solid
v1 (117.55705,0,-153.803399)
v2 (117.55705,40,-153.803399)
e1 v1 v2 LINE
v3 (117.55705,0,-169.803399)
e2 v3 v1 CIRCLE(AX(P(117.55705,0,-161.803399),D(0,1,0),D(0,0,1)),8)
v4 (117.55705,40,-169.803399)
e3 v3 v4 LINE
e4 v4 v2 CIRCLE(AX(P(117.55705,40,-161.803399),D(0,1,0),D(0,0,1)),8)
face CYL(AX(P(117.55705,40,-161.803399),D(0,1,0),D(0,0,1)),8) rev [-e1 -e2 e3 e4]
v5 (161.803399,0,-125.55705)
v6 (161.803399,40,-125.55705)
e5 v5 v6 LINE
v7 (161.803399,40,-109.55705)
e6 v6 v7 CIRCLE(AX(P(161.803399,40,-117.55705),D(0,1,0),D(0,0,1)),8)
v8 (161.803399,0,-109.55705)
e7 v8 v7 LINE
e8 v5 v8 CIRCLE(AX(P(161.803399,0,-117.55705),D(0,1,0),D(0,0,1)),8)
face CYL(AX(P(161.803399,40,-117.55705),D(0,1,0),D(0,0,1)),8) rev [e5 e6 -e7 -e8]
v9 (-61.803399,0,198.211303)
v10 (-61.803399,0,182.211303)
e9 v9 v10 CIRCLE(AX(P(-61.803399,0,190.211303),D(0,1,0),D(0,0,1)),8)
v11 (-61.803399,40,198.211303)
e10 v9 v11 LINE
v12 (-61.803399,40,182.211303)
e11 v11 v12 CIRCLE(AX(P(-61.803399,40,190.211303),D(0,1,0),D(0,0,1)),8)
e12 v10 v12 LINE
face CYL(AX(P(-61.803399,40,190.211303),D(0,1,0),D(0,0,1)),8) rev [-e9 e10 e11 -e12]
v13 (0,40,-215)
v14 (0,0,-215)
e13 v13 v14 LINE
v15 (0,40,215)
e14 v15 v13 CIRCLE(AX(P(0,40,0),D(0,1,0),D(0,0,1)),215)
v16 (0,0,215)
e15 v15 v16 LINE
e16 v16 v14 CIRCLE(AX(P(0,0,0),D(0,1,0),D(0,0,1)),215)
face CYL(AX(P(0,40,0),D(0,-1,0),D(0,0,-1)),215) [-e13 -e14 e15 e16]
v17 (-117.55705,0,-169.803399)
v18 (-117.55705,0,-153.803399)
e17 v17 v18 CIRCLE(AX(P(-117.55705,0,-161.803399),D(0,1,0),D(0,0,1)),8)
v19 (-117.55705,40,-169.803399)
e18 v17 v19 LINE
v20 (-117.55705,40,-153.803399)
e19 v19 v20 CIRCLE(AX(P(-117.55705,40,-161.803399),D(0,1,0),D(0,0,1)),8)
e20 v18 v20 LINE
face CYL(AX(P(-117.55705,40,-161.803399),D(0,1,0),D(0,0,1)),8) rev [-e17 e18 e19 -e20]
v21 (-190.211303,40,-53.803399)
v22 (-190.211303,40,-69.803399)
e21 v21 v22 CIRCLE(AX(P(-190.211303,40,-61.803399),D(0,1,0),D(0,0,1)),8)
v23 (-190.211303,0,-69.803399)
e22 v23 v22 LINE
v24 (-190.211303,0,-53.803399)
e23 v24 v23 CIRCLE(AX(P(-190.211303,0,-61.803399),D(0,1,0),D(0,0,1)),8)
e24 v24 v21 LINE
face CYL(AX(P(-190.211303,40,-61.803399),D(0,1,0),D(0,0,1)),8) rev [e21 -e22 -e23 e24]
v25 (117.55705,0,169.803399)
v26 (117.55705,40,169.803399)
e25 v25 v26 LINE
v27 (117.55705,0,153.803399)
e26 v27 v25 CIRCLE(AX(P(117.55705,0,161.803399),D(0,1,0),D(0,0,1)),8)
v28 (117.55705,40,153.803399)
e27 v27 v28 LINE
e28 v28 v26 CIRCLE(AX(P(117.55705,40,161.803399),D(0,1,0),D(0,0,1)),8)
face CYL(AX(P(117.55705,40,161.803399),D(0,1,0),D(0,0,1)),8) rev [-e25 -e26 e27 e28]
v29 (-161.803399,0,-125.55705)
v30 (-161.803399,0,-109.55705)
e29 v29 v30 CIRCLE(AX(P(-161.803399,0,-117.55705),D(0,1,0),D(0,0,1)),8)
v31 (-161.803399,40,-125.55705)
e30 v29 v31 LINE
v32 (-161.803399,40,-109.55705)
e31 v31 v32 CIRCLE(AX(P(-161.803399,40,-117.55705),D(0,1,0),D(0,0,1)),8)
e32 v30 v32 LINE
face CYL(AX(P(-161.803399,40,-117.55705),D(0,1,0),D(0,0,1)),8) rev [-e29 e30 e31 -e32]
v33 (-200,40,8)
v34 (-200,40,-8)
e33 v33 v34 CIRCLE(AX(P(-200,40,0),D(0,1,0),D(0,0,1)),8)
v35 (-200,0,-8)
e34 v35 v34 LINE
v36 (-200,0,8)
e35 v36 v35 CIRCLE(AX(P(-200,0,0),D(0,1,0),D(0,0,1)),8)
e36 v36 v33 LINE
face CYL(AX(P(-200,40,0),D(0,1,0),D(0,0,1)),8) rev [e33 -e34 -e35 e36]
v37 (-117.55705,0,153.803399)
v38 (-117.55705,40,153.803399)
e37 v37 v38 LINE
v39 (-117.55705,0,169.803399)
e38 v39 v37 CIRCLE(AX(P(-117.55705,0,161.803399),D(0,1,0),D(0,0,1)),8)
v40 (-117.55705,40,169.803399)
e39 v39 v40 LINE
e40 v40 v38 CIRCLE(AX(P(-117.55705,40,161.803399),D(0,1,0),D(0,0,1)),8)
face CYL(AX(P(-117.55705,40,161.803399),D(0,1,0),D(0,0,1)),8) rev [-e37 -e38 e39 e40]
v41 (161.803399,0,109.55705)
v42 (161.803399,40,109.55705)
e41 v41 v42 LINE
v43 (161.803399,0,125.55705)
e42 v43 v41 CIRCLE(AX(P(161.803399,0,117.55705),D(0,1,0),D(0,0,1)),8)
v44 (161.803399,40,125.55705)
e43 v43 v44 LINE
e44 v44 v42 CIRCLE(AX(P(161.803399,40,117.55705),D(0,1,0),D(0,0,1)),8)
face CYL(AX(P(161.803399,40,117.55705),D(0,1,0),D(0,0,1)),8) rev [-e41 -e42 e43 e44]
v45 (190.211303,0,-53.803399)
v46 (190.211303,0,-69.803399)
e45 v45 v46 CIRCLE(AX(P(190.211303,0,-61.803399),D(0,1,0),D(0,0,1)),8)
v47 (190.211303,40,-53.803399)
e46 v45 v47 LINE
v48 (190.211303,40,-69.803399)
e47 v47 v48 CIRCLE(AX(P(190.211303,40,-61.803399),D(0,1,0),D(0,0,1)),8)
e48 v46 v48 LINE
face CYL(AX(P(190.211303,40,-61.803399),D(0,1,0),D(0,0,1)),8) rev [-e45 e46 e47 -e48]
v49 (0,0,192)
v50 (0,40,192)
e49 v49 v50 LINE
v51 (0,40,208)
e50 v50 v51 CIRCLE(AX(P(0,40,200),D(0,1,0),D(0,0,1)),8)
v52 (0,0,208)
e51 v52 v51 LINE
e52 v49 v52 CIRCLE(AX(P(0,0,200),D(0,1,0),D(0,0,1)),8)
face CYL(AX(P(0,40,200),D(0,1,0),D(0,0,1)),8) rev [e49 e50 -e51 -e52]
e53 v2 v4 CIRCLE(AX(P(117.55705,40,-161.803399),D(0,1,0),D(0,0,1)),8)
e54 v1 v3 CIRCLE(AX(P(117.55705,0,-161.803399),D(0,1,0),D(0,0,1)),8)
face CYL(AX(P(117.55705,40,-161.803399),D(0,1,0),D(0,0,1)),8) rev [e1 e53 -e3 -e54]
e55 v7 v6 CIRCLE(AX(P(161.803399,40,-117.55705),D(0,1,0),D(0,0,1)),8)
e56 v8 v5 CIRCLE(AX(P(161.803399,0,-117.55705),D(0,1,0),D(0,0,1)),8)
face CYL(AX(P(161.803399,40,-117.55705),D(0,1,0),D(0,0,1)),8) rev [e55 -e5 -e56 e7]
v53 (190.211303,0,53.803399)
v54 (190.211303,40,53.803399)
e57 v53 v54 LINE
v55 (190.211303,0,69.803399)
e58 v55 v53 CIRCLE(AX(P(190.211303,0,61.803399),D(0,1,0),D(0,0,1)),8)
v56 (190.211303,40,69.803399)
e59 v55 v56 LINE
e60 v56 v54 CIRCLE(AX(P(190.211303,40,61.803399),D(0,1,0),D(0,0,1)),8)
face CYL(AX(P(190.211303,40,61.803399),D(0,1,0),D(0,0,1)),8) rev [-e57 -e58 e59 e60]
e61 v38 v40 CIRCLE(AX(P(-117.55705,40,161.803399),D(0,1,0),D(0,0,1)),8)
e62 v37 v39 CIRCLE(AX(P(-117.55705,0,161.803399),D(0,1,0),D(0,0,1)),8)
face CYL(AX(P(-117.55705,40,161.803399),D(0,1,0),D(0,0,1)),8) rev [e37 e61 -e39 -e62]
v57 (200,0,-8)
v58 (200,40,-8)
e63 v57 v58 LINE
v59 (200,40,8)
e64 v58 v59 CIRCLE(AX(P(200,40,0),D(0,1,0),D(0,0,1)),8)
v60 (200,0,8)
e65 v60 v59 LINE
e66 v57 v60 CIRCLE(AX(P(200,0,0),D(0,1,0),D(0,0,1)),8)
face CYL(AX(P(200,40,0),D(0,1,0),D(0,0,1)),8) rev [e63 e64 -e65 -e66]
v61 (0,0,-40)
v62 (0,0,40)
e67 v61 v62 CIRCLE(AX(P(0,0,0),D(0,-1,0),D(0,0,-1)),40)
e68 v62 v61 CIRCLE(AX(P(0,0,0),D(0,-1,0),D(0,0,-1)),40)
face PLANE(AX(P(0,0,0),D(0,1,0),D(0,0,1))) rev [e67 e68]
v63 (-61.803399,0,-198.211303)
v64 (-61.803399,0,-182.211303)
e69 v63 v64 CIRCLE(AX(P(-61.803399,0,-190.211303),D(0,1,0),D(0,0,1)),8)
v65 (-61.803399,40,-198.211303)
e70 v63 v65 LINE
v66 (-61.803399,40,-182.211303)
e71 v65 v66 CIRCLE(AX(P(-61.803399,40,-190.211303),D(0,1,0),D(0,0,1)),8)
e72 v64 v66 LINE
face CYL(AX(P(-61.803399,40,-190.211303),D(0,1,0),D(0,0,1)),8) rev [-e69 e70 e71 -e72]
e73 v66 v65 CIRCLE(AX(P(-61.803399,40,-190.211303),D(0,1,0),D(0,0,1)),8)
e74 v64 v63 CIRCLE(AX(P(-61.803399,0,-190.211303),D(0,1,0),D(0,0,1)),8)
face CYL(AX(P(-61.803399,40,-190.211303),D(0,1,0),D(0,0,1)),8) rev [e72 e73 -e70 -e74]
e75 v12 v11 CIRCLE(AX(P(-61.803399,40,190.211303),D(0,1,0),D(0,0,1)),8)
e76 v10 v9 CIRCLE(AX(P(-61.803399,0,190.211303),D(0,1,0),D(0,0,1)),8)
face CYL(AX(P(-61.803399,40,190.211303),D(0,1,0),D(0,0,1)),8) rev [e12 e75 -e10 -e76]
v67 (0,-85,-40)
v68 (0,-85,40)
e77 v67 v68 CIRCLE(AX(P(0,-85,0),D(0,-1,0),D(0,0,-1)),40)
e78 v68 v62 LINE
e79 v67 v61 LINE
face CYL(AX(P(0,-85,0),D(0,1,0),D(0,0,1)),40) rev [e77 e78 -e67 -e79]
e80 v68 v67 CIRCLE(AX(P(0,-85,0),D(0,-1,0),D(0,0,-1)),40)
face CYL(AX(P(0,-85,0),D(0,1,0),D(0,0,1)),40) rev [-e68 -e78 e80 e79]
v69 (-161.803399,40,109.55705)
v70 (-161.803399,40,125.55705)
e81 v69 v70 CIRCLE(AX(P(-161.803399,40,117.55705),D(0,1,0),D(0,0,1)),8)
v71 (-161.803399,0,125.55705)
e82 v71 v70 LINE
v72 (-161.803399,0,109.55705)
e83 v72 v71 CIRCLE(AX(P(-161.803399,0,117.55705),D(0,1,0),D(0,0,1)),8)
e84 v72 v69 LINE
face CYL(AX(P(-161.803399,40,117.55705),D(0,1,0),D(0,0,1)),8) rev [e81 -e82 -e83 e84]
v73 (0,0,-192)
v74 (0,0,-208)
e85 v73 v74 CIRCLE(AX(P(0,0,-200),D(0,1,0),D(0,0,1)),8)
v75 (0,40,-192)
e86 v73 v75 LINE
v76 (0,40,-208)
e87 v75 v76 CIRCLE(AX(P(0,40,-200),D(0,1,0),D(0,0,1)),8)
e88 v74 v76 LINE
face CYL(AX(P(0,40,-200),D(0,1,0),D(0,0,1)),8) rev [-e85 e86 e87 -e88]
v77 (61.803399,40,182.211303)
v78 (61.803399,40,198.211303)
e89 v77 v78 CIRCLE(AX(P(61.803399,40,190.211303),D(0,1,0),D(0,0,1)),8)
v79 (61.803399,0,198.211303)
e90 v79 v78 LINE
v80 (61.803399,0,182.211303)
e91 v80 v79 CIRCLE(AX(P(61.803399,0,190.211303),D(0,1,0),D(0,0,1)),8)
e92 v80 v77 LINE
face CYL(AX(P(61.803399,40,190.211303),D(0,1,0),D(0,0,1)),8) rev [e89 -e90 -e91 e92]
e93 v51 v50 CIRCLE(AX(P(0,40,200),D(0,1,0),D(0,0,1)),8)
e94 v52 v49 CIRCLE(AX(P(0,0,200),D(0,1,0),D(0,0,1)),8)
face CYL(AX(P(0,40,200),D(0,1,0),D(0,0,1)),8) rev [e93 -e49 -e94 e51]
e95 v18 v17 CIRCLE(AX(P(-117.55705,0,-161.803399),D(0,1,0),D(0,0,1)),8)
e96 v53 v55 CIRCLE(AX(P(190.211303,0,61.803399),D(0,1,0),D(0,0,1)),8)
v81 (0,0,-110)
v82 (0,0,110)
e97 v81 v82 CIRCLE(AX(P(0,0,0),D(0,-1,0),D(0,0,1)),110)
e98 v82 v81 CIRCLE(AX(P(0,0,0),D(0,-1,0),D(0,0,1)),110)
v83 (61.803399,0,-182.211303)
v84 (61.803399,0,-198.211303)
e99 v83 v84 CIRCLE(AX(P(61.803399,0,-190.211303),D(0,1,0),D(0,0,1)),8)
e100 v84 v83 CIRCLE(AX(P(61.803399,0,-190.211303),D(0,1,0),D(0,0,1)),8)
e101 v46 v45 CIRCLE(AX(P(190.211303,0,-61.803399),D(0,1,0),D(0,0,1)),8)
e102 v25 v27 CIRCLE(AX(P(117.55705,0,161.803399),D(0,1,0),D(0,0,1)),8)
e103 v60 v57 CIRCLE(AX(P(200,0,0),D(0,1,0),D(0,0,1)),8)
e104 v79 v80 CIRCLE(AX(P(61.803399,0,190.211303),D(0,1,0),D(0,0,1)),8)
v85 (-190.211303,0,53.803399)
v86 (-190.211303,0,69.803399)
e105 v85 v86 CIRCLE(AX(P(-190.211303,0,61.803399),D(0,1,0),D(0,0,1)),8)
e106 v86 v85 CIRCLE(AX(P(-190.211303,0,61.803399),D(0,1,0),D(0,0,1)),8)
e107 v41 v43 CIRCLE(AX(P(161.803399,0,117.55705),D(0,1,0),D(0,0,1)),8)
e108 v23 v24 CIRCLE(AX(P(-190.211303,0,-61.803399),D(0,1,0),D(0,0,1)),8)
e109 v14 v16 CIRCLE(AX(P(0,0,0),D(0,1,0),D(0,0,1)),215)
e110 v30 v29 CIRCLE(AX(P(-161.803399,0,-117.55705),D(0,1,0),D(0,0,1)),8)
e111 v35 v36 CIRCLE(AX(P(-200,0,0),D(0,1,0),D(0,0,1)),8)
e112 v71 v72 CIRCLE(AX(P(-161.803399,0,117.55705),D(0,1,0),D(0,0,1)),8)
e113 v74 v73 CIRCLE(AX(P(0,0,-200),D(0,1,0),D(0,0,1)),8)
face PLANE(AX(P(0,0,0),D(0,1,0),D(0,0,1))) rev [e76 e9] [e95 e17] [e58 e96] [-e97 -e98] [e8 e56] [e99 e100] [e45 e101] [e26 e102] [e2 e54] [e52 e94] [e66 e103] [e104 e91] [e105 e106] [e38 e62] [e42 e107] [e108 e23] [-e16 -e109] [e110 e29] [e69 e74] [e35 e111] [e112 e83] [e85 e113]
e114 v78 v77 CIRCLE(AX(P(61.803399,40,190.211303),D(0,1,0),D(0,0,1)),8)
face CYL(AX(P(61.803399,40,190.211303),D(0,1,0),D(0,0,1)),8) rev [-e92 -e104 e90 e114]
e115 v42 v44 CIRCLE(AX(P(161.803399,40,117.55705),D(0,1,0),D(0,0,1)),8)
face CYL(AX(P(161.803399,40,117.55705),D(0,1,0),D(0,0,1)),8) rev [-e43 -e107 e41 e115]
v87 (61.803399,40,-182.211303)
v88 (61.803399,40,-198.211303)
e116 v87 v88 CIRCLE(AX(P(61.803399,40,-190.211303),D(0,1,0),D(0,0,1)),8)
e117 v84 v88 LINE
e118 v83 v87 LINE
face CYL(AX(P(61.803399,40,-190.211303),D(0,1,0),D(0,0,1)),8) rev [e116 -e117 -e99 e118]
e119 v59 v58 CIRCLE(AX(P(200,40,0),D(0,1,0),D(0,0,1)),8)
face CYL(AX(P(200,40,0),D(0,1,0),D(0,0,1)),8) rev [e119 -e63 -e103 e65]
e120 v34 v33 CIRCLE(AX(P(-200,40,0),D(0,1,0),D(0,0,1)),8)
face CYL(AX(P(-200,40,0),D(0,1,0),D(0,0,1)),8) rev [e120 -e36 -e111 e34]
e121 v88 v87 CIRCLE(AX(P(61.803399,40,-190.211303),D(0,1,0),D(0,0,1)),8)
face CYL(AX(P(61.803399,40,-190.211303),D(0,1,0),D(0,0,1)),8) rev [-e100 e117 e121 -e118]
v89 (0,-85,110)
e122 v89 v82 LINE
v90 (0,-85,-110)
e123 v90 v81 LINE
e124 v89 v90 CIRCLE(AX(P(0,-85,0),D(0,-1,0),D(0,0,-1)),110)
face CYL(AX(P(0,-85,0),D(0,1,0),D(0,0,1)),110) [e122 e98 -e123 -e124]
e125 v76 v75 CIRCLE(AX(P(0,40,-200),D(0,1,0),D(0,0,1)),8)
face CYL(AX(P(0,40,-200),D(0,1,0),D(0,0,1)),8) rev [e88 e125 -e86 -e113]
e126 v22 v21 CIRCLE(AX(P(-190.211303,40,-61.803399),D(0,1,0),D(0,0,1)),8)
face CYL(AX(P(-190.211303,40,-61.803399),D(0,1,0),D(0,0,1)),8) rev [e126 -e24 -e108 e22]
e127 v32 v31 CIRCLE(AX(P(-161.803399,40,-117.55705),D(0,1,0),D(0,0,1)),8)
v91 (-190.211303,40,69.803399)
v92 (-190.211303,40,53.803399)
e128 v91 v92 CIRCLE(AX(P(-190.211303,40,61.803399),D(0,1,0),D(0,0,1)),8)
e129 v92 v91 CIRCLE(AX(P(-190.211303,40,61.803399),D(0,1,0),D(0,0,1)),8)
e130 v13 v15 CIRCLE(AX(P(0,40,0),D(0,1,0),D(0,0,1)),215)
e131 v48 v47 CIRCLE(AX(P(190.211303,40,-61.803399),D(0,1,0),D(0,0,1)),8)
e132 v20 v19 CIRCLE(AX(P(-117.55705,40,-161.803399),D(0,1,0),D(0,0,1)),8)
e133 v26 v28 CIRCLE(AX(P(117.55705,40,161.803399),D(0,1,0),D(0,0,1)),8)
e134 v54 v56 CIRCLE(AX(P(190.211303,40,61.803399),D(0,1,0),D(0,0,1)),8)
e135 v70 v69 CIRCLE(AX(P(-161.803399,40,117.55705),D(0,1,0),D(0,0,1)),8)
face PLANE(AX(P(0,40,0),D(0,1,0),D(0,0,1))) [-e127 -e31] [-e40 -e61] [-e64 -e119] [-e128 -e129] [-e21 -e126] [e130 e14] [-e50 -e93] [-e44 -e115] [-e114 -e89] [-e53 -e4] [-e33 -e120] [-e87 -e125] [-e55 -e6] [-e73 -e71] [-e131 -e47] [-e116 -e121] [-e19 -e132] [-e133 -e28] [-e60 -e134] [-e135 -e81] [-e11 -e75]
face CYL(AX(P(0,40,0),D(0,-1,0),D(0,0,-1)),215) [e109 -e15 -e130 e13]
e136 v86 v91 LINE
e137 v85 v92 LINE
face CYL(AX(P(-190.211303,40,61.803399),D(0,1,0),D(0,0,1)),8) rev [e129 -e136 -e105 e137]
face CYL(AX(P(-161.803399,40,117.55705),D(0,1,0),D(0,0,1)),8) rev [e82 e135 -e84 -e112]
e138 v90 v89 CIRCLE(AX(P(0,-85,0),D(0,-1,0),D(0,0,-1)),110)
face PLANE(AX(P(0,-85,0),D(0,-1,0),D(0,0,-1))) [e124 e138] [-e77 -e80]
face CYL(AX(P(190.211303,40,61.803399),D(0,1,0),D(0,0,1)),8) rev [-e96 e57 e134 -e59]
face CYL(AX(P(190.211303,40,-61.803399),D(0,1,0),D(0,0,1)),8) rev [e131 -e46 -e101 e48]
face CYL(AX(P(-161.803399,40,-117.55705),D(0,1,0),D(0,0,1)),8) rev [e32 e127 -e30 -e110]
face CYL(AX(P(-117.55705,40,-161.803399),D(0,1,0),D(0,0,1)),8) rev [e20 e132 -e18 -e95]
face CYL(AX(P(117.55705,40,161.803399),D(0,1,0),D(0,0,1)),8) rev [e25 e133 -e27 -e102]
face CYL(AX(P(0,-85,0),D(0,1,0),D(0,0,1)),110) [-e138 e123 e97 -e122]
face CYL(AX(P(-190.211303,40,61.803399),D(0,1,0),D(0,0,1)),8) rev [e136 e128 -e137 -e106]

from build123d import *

# Parameters (mm, degrees)
SKETCH1_R                  = 215
BOSS_EXTRUDE1_DEPTH        = 40
F_16_0_16_DIAMETER_HOLE1_D = 16
SKETCH7_R                  = 110
SKETCH7_R_2                = 40
BOSS_EXTRUDE2_DEPTH        = 85


with BuildPart() as part:
    # Sketch1 → Boss-Extrude1 (new body)
    with BuildSketch(Plane(origin=(0, 0, 0), x_dir=(1, 0, 0), z_dir=(0, 1, 0))):
        with Locations(Location((0, 0, 0), (0, 0, 270))):
            Circle(SKETCH1_R)
    extrude(amount=BOSS_EXTRUDE1_DEPTH)

    # Ø16.0 (16) Diameter Hole1 (through all)
    with Locations(Plane(origin=(0, 40, 0), x_dir=(1, 0, 0), z_dir=(0, 1, 0))):
        with Locations((200, 0), (190.211303259, -61.803398875), (161.803398875, -117.557050458), (117.557050458, -161.803398875), (61.803398875, -190.211303259), (0, -200), (-61.803398875, -190.211303259), (-117.557050458, -161.803398875), (-161.803398875, -117.557050458), (-190.211303259, -61.803398875), (-200, 0), (-190.211303259, 61.803398875), (-161.803398875, 117.557050458), (-117.557050458, 161.803398875), (-61.803398875, 190.211303259), (0, 200), (61.803398875, 190.211303259), (117.557050458, 161.803398875), (161.803398875, 117.557050458), (190.211303259, 61.803398875)):
            Hole(F_16_0_16_DIAMETER_HOLE1_D / 2)

    # Sketch7 → Boss-Extrude2 (add)
    with BuildSketch(Plane.XZ):
        with Locations(Location((0, 0, 0), (0, 0, 90))):
            Circle(SKETCH7_R)
        with Locations(Location((0, 0, 0), (0, 0, 270))):
            Circle(SKETCH7_R_2, mode=Mode.SUBTRACT)
    extrude(amount=BOSS_EXTRUDE2_DEPTH)


solid = part.part
